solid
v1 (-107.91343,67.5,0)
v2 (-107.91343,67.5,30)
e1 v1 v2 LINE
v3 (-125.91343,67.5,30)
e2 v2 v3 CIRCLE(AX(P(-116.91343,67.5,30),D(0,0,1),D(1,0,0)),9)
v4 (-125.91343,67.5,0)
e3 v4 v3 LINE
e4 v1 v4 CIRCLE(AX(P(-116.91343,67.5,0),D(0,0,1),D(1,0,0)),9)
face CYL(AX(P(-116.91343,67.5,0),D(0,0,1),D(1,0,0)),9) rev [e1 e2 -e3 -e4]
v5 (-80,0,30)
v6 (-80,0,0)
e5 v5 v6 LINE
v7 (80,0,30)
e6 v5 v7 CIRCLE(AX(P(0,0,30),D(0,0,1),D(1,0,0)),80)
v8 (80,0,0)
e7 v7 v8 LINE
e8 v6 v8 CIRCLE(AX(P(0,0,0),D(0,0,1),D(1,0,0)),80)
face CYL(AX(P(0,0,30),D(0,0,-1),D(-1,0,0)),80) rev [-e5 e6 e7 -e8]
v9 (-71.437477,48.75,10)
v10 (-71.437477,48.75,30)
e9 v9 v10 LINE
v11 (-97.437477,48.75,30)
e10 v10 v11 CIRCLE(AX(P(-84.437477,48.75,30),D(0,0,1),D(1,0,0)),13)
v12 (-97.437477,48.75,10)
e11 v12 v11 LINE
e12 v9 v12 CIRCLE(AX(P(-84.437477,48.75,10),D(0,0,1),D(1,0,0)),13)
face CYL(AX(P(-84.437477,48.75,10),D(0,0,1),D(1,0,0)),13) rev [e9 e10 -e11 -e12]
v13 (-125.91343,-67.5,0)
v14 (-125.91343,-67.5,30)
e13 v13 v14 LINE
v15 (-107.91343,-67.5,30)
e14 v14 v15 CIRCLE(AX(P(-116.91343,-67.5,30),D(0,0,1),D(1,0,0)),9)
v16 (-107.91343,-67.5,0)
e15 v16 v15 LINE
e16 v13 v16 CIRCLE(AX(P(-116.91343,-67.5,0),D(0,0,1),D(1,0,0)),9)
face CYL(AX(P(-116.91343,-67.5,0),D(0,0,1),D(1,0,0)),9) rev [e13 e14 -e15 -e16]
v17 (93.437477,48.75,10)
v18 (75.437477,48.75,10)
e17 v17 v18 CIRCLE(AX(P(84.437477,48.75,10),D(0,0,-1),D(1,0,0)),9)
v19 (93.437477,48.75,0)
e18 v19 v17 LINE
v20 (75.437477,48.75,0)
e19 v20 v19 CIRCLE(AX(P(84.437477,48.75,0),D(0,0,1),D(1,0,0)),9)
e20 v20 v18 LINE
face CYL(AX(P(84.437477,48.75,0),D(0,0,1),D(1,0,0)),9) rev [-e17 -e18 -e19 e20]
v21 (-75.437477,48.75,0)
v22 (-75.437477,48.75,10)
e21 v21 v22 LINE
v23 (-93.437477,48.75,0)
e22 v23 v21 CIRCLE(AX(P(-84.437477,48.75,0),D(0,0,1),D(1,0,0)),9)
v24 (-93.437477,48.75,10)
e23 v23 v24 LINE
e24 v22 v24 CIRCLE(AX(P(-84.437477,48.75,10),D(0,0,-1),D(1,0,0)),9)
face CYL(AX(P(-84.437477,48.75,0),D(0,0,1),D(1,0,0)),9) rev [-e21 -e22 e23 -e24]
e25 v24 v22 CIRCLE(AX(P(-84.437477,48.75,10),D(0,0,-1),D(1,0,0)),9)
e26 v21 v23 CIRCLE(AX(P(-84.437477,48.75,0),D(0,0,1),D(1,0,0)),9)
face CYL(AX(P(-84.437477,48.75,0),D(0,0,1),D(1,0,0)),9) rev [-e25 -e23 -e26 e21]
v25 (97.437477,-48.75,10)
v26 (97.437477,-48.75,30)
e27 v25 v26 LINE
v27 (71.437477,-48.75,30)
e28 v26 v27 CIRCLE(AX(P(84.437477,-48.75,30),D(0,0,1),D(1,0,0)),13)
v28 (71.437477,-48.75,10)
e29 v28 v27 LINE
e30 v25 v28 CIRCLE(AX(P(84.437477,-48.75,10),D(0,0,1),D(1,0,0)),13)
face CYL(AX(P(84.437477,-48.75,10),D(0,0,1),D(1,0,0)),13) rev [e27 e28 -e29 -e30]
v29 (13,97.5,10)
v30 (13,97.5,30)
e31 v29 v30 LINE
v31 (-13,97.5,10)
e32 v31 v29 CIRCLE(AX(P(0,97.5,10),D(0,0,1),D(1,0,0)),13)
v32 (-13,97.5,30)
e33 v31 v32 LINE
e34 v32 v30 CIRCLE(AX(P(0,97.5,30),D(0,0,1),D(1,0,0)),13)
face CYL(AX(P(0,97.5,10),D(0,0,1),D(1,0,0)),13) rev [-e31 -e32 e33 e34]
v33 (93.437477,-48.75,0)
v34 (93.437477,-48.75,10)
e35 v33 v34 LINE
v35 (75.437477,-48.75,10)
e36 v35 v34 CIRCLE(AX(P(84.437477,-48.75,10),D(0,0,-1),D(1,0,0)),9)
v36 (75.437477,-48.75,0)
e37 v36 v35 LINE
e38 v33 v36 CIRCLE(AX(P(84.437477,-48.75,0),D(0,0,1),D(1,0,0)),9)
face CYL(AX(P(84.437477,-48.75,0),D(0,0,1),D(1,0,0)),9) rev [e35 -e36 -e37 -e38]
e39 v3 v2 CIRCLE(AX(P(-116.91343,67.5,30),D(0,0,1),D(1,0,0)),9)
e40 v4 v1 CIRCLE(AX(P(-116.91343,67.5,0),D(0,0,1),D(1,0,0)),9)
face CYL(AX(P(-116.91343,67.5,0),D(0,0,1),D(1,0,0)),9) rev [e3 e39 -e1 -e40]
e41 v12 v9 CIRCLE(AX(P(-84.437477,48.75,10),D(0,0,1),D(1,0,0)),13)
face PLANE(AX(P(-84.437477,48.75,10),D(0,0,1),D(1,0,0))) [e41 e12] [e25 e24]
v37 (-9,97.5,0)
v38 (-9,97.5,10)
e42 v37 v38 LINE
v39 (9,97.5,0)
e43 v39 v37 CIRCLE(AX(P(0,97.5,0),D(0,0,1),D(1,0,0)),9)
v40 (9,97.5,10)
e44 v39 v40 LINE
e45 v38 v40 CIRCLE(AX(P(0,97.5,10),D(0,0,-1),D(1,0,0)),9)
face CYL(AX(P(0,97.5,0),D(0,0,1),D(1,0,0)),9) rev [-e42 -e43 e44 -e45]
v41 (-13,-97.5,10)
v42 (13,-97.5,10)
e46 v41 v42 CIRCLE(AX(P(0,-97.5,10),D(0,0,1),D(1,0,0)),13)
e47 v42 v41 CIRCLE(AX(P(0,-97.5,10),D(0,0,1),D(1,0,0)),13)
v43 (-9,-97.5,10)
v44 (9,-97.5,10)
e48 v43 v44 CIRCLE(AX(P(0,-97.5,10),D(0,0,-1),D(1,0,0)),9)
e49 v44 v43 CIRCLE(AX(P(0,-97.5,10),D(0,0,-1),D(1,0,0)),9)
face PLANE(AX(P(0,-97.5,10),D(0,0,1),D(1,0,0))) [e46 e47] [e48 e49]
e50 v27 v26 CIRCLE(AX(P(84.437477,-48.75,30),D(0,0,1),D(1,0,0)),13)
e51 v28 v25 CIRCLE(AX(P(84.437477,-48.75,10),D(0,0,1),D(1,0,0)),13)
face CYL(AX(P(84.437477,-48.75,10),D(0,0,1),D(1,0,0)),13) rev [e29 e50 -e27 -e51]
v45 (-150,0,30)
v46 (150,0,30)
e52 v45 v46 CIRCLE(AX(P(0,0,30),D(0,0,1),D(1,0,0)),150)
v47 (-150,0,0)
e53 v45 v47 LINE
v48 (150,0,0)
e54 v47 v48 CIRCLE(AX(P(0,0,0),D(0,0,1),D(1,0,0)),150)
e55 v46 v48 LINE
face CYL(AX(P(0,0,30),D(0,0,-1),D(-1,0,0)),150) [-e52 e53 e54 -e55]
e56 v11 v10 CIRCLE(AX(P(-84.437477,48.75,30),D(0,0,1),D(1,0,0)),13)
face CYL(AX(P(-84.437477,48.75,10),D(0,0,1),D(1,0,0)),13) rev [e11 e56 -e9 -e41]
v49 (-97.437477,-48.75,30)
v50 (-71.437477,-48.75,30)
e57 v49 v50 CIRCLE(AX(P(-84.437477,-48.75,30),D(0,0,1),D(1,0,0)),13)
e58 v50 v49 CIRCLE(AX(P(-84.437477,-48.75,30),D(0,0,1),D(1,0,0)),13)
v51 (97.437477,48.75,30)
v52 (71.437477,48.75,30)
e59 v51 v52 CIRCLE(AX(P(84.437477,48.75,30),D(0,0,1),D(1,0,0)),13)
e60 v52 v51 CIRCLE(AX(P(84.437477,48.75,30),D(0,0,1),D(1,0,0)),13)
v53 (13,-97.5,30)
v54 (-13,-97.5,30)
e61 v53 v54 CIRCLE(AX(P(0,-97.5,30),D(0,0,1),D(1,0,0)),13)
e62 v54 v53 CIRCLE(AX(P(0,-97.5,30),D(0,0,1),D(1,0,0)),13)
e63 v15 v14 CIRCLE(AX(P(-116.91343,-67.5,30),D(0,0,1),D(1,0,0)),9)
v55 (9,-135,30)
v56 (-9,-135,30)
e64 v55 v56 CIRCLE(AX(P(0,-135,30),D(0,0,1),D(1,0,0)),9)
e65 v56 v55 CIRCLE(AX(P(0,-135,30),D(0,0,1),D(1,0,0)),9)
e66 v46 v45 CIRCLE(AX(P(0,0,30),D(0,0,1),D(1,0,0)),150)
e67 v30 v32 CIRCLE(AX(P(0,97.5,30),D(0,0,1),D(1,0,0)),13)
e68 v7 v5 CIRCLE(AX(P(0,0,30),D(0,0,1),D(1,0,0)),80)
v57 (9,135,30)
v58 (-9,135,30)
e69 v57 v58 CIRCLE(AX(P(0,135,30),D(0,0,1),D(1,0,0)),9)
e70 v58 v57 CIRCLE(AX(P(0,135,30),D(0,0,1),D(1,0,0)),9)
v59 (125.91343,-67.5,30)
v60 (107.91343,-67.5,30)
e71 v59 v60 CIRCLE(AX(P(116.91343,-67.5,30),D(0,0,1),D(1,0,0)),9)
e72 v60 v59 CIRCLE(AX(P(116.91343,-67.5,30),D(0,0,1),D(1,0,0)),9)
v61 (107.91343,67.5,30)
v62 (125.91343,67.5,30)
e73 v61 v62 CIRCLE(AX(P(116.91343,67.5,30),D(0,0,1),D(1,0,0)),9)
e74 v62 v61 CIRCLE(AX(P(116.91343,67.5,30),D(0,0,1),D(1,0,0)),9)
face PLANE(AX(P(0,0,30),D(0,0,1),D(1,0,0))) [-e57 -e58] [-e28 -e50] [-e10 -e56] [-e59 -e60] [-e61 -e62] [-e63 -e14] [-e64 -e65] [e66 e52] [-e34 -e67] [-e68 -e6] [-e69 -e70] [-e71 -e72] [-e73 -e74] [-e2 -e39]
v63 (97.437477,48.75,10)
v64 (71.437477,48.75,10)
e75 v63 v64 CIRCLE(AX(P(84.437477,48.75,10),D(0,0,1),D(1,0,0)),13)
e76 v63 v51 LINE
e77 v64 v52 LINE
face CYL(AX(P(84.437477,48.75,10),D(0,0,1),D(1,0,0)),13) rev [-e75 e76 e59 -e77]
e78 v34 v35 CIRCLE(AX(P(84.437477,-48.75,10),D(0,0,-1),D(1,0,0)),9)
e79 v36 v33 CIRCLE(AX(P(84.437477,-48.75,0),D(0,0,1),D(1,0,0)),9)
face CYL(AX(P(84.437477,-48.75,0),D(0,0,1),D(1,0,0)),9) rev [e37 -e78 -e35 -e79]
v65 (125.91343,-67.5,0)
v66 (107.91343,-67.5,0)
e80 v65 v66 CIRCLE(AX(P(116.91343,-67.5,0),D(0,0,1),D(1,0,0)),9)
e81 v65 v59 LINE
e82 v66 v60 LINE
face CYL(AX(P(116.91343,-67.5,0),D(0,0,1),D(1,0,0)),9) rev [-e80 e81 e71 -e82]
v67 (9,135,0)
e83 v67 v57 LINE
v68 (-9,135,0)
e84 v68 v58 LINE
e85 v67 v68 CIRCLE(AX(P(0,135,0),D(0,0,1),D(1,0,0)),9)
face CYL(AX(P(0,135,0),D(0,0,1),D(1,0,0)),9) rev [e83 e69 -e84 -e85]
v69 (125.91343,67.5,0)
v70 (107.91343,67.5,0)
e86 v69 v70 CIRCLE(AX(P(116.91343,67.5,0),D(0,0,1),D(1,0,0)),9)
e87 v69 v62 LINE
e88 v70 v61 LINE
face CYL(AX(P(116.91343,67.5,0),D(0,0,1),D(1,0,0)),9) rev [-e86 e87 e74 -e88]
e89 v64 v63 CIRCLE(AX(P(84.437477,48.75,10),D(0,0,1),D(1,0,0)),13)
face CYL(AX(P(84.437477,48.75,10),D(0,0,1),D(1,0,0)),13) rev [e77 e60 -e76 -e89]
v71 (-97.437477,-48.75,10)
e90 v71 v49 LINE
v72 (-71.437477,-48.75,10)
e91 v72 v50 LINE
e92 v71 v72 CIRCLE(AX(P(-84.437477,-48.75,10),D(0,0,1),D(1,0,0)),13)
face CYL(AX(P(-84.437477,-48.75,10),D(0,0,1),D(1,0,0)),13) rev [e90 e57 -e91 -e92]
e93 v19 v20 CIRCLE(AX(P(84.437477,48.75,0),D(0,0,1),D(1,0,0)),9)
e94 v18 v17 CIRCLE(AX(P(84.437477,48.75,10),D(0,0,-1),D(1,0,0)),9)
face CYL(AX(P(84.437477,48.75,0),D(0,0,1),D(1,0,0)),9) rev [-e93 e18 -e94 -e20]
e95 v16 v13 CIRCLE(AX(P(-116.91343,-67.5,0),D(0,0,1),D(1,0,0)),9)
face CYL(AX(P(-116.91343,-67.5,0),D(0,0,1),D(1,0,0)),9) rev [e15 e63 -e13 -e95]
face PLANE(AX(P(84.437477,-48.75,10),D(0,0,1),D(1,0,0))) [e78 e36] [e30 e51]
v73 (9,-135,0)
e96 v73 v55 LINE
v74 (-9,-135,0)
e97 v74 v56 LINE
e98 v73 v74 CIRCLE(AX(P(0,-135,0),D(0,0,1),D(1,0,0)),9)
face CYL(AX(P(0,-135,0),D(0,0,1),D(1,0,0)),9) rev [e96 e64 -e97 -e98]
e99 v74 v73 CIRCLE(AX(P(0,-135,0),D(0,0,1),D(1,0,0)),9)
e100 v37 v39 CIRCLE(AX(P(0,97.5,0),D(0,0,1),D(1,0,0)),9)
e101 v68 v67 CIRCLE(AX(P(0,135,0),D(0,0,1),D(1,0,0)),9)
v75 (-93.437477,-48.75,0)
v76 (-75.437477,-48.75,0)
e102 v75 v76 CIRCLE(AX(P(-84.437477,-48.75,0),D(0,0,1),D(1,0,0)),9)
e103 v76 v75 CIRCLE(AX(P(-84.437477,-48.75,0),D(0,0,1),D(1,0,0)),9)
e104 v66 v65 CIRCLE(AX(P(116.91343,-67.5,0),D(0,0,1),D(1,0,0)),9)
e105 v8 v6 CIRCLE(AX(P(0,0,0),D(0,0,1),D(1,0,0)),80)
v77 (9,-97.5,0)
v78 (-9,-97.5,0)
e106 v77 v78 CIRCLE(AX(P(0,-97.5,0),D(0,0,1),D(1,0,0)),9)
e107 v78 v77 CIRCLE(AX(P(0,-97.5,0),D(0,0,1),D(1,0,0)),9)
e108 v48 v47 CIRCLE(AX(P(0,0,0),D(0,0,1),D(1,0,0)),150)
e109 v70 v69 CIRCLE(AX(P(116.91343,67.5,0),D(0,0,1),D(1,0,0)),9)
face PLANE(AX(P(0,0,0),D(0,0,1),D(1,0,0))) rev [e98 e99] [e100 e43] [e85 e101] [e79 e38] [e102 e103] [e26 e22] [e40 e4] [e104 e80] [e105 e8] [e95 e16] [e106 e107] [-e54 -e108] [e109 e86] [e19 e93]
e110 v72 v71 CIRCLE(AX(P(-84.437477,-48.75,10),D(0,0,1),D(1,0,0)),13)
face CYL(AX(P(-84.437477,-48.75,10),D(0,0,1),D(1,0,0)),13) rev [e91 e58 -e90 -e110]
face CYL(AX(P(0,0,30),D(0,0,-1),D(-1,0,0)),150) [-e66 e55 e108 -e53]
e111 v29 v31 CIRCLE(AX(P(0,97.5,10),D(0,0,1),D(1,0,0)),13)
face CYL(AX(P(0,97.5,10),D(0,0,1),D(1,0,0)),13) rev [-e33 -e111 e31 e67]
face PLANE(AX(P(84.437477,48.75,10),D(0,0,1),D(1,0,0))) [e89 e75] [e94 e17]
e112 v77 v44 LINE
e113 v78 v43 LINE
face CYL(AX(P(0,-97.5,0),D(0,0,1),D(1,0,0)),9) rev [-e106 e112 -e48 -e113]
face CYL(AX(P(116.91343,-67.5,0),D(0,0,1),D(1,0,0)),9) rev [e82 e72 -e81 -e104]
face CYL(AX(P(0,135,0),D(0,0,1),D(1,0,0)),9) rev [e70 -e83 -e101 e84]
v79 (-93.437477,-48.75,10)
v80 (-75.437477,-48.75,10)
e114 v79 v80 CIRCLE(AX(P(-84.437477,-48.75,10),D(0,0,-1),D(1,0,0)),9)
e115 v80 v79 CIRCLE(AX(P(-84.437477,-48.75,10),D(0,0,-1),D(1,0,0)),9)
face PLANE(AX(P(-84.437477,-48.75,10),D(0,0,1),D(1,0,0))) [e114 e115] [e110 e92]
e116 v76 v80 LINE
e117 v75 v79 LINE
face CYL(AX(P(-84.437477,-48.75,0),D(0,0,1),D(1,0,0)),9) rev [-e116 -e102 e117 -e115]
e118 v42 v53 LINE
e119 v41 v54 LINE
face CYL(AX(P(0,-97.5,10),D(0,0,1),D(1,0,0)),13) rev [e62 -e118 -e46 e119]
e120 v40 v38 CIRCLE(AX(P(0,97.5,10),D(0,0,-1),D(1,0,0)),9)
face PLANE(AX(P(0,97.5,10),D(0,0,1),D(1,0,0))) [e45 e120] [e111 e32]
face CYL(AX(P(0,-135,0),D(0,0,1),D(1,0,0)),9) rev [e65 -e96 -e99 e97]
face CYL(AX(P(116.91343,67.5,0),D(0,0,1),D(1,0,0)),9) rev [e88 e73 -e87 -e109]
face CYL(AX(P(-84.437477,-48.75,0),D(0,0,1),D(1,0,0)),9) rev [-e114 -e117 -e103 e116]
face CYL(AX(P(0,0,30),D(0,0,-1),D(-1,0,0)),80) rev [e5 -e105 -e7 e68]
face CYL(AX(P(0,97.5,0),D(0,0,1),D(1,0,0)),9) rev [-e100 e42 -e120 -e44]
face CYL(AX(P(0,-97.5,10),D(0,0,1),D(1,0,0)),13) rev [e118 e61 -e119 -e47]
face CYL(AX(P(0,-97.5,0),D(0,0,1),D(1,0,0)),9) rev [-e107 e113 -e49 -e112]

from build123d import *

# Parameters (mm, degrees)
SKETCH1_R           = 150
SKETCH1_R_2         = 80
BOSS_EXTRUDE1_DEPTH = 30
SKETCH2_R           = 9
CUT_EXTRUDE1_DEPTH  = 30
SKETCH3_R           = 9
CUT_EXTRUDE2_DEPTH  = 215.242852856
SKETCH4_R           = 13
CUT_EXTRUDE3_DEPTH  = 20


with BuildPart() as part:
    # Sketch1 → Boss-Extrude1 (new body)
    with BuildSketch(Plane.XY):
        Circle(SKETCH1_R)
        Circle(SKETCH1_R_2, mode=Mode.SUBTRACT)
    extrude(amount=BOSS_EXTRUDE1_DEPTH)

    # Sketch2 → Cut-Extrude1 (cut)
    with BuildSketch(Plane.XY.offset(30)):
        with Locations((0, 135)):
            Circle(SKETCH2_R)
        with Locations((116.913429511, 67.5)):
            Circle(SKETCH2_R)
        with Locations((116.913429511, -67.5)):
            Circle(SKETCH2_R)
        with Locations((0, -135)):
            Circle(SKETCH2_R)
        with Locations((-116.913429511, -67.5)):
            Circle(SKETCH2_R)
        with Locations((-116.913429511, 67.5)):
            Circle(SKETCH2_R)
    extrude(amount=-CUT_EXTRUDE1_DEPTH, mode=Mode.SUBTRACT)

    # Sketch3 → Cut-Extrude2 (cut, through all)
    with BuildSketch(Plane.XY.offset(30)):
        with Locations((0, 97.5)):
            Circle(SKETCH3_R)
        with Locations((84.437476869, 48.75)):
            Circle(SKETCH3_R)
        with Locations((84.437476869, -48.75)):
            Circle(SKETCH3_R)
        with Locations((0, -97.5)):
            Circle(SKETCH3_R)
        with Locations((-84.437476869, -48.75)):
            Circle(SKETCH3_R)
        with Locations((-84.437476869, 48.75)):
            Circle(SKETCH3_R)
    extrude(amount=-CUT_EXTRUDE2_DEPTH, mode=Mode.SUBTRACT)

    # Sketch4 → Cut-Extrude3 (cut)
    with BuildSketch(Plane.XY.offset(30)):
        with Locations((0, 97.5)):
            Circle(SKETCH4_R)
        with Locations((84.437476869, 48.75)):
            Circle(SKETCH4_R)
        with Locations((84.437476869, -48.75)):
            Circle(SKETCH4_R)
        with Locations((0, -97.5)):
            Circle(SKETCH4_R)
        with Locations((-84.437476869, -48.75)):
            Circle(SKETCH4_R)
        with Locations((-84.437476869, 48.75)):
            Circle(SKETCH4_R)
    extrude(amount=-CUT_EXTRUDE3_DEPTH, mode=Mode.SUBTRACT)


solid = part.part
